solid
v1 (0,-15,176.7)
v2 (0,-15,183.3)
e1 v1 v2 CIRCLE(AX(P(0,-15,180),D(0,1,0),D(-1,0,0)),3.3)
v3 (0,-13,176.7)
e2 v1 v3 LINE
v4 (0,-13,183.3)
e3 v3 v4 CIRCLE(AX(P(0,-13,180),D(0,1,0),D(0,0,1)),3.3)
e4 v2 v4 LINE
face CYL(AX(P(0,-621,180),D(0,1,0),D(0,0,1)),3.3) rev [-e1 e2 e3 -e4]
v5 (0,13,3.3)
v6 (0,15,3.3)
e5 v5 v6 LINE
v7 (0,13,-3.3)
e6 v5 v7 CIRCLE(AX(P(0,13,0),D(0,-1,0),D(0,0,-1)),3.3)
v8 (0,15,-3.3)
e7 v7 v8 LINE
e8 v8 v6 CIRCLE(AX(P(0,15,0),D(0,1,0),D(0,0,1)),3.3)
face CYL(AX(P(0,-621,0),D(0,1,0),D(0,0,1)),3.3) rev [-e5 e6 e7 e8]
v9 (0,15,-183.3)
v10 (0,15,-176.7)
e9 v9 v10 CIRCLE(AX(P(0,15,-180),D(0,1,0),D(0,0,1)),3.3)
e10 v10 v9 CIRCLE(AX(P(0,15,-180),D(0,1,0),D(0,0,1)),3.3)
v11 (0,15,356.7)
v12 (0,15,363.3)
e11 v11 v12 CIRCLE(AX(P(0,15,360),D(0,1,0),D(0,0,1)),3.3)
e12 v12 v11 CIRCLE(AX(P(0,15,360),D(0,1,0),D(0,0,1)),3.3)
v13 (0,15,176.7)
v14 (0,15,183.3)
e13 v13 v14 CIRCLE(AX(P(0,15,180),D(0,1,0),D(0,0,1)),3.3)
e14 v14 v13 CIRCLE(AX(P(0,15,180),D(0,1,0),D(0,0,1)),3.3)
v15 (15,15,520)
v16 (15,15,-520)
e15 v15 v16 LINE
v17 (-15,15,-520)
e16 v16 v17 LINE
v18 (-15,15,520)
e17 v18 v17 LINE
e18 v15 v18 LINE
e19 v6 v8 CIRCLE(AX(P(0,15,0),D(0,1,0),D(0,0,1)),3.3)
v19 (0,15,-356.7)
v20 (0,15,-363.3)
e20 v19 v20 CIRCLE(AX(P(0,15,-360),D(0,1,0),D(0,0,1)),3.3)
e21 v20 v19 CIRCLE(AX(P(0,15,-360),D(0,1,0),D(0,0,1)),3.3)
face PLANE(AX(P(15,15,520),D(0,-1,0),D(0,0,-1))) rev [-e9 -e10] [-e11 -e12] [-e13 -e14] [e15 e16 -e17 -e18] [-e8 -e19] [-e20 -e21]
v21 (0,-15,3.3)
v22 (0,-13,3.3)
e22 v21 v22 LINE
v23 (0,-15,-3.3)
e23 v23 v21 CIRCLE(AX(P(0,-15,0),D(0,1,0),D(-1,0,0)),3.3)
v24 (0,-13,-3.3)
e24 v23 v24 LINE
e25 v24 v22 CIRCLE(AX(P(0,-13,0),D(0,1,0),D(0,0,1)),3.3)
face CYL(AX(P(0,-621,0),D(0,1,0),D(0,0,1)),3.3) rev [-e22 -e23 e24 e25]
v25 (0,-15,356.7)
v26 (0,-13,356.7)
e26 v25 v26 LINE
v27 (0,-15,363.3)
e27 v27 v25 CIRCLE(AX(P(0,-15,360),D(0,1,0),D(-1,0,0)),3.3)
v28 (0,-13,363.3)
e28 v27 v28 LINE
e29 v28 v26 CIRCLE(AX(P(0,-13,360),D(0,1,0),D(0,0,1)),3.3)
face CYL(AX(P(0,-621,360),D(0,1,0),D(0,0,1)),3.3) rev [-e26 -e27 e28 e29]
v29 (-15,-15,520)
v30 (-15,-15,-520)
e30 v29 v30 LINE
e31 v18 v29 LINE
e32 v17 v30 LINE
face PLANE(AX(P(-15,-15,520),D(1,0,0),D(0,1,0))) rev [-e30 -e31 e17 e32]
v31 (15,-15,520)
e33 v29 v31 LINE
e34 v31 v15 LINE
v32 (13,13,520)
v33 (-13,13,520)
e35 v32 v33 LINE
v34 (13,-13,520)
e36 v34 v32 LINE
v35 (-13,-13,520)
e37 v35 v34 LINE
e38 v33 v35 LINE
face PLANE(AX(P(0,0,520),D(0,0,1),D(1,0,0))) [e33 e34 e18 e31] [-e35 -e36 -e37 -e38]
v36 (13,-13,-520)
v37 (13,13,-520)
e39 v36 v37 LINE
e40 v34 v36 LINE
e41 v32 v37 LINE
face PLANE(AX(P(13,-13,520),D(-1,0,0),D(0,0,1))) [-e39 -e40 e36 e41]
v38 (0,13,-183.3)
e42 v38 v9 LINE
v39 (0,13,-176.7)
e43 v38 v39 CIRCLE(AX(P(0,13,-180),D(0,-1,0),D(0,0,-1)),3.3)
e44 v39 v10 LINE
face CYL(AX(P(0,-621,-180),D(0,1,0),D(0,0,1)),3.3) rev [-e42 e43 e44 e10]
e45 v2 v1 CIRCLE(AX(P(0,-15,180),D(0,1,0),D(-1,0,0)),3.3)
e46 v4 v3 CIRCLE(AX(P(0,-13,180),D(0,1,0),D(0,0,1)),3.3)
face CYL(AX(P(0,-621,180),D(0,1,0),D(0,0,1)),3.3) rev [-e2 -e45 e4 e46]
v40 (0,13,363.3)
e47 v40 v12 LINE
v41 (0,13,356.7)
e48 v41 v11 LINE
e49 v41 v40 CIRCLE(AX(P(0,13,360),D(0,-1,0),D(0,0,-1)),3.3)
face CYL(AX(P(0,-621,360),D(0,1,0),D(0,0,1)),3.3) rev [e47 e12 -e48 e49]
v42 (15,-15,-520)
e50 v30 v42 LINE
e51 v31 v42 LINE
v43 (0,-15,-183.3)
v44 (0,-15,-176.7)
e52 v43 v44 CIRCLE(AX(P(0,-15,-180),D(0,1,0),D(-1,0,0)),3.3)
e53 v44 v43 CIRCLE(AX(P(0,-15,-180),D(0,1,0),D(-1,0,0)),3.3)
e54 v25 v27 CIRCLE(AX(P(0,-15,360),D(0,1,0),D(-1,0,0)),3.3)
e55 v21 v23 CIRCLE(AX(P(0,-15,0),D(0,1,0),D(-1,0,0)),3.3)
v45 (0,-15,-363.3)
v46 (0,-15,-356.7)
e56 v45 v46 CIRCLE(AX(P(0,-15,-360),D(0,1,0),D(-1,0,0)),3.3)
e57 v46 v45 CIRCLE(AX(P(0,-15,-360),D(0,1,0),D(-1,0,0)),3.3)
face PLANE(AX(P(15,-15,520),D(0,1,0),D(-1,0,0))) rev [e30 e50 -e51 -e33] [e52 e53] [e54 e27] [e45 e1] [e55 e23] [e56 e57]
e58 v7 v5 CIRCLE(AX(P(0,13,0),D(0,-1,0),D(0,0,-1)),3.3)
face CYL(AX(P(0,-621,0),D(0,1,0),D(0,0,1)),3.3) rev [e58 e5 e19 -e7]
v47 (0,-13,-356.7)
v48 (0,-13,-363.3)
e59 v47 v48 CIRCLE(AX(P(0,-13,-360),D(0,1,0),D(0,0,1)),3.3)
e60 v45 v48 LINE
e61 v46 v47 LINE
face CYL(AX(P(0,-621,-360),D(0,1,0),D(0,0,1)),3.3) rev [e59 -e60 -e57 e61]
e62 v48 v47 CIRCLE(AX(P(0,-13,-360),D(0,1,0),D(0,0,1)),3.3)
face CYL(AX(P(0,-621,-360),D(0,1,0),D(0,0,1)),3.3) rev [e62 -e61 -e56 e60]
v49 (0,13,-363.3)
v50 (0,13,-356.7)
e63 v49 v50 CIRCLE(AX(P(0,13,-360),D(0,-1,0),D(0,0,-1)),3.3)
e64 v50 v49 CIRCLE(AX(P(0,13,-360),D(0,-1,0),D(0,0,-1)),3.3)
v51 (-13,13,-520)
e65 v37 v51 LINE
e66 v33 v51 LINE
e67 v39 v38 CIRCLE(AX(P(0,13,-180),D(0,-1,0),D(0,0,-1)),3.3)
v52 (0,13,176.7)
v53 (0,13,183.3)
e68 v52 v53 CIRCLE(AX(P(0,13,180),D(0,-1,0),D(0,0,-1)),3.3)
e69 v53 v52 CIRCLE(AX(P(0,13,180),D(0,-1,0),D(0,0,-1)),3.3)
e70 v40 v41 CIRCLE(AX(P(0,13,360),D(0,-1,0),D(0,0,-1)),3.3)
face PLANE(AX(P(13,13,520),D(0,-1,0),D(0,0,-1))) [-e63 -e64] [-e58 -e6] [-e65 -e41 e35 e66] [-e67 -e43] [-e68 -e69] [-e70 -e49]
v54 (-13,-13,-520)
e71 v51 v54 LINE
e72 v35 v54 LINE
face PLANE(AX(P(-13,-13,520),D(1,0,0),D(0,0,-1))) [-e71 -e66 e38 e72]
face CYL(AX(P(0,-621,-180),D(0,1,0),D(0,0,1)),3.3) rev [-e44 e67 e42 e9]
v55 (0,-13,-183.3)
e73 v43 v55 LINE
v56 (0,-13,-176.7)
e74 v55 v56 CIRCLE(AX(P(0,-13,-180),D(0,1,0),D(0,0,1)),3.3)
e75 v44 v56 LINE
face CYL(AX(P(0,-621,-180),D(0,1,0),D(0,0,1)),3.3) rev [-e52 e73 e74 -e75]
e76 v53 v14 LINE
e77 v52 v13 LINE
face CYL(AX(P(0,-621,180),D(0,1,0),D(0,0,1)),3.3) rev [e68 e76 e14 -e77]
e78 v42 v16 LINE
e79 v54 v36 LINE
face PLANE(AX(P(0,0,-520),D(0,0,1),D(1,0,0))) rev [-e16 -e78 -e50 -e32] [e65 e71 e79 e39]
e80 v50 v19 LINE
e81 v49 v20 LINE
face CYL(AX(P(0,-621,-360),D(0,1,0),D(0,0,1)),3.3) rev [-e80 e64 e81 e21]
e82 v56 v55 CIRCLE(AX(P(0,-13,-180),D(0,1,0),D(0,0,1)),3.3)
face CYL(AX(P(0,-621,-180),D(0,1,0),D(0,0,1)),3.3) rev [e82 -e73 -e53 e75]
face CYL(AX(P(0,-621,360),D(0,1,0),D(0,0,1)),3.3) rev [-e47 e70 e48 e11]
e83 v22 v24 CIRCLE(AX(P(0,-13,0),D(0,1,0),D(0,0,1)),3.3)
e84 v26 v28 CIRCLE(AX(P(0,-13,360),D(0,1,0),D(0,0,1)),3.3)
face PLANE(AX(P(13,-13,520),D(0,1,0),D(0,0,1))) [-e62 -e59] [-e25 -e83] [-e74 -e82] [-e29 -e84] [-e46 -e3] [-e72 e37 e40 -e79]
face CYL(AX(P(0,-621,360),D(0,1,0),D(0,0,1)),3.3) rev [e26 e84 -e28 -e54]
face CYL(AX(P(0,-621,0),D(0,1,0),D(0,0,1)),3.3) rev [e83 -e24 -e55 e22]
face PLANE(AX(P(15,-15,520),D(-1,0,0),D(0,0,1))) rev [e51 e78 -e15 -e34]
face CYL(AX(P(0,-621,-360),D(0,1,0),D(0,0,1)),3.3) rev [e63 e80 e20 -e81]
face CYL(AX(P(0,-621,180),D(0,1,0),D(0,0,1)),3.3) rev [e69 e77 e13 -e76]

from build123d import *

# Parameters (mm, degrees)
SKETCH_1_W          = 30
SKETCH_1_H          = 30
SKETCH_1_W_2        = 26
SKETCH_1_H_2        = 26
EXTRUDE_1_DEPTH     = 520
SKETCH_3_R          = 3.3
CUT_EXTRUDE_1_DEPTH = 636


with BuildPart() as part:
    # 草图1 → 凸台-拉伸1 (new, symmetric)
    with BuildSketch(Plane.XY):
        Rectangle(SKETCH_1_W, SKETCH_1_H)
        Rectangle(SKETCH_1_W_2, SKETCH_1_H_2, mode=Mode.SUBTRACT)
    extrude(amount=EXTRUDE_1_DEPTH, both=True)

    # 草图3 → 切除-拉伸1 (cut)
    with BuildSketch(Plane(origin=(0, 15, 0), x_dir=(1, 0, 0), z_dir=(0, 1, 0))):
        with Locations(Location((0, 360, 0), (0, 0, 270))):
            Circle(SKETCH_3_R)
        with Locations(Location((0, 180, 0), (0, 0, 270))):
            Circle(SKETCH_3_R)
        with Locations(Location((0, 0, 0), (0, 0, 270))):
            Circle(SKETCH_3_R)
        with Locations(Location((0, -180, 0), (0, 0, 270))):
            Circle(SKETCH_3_R)
        with Locations(Location((0, -360, 0), (0, 0, 270))):
            Circle(SKETCH_3_R)
    extrude(amount=-CUT_EXTRUDE_1_DEPTH, mode=Mode.SUBTRACT)


solid = part.part
